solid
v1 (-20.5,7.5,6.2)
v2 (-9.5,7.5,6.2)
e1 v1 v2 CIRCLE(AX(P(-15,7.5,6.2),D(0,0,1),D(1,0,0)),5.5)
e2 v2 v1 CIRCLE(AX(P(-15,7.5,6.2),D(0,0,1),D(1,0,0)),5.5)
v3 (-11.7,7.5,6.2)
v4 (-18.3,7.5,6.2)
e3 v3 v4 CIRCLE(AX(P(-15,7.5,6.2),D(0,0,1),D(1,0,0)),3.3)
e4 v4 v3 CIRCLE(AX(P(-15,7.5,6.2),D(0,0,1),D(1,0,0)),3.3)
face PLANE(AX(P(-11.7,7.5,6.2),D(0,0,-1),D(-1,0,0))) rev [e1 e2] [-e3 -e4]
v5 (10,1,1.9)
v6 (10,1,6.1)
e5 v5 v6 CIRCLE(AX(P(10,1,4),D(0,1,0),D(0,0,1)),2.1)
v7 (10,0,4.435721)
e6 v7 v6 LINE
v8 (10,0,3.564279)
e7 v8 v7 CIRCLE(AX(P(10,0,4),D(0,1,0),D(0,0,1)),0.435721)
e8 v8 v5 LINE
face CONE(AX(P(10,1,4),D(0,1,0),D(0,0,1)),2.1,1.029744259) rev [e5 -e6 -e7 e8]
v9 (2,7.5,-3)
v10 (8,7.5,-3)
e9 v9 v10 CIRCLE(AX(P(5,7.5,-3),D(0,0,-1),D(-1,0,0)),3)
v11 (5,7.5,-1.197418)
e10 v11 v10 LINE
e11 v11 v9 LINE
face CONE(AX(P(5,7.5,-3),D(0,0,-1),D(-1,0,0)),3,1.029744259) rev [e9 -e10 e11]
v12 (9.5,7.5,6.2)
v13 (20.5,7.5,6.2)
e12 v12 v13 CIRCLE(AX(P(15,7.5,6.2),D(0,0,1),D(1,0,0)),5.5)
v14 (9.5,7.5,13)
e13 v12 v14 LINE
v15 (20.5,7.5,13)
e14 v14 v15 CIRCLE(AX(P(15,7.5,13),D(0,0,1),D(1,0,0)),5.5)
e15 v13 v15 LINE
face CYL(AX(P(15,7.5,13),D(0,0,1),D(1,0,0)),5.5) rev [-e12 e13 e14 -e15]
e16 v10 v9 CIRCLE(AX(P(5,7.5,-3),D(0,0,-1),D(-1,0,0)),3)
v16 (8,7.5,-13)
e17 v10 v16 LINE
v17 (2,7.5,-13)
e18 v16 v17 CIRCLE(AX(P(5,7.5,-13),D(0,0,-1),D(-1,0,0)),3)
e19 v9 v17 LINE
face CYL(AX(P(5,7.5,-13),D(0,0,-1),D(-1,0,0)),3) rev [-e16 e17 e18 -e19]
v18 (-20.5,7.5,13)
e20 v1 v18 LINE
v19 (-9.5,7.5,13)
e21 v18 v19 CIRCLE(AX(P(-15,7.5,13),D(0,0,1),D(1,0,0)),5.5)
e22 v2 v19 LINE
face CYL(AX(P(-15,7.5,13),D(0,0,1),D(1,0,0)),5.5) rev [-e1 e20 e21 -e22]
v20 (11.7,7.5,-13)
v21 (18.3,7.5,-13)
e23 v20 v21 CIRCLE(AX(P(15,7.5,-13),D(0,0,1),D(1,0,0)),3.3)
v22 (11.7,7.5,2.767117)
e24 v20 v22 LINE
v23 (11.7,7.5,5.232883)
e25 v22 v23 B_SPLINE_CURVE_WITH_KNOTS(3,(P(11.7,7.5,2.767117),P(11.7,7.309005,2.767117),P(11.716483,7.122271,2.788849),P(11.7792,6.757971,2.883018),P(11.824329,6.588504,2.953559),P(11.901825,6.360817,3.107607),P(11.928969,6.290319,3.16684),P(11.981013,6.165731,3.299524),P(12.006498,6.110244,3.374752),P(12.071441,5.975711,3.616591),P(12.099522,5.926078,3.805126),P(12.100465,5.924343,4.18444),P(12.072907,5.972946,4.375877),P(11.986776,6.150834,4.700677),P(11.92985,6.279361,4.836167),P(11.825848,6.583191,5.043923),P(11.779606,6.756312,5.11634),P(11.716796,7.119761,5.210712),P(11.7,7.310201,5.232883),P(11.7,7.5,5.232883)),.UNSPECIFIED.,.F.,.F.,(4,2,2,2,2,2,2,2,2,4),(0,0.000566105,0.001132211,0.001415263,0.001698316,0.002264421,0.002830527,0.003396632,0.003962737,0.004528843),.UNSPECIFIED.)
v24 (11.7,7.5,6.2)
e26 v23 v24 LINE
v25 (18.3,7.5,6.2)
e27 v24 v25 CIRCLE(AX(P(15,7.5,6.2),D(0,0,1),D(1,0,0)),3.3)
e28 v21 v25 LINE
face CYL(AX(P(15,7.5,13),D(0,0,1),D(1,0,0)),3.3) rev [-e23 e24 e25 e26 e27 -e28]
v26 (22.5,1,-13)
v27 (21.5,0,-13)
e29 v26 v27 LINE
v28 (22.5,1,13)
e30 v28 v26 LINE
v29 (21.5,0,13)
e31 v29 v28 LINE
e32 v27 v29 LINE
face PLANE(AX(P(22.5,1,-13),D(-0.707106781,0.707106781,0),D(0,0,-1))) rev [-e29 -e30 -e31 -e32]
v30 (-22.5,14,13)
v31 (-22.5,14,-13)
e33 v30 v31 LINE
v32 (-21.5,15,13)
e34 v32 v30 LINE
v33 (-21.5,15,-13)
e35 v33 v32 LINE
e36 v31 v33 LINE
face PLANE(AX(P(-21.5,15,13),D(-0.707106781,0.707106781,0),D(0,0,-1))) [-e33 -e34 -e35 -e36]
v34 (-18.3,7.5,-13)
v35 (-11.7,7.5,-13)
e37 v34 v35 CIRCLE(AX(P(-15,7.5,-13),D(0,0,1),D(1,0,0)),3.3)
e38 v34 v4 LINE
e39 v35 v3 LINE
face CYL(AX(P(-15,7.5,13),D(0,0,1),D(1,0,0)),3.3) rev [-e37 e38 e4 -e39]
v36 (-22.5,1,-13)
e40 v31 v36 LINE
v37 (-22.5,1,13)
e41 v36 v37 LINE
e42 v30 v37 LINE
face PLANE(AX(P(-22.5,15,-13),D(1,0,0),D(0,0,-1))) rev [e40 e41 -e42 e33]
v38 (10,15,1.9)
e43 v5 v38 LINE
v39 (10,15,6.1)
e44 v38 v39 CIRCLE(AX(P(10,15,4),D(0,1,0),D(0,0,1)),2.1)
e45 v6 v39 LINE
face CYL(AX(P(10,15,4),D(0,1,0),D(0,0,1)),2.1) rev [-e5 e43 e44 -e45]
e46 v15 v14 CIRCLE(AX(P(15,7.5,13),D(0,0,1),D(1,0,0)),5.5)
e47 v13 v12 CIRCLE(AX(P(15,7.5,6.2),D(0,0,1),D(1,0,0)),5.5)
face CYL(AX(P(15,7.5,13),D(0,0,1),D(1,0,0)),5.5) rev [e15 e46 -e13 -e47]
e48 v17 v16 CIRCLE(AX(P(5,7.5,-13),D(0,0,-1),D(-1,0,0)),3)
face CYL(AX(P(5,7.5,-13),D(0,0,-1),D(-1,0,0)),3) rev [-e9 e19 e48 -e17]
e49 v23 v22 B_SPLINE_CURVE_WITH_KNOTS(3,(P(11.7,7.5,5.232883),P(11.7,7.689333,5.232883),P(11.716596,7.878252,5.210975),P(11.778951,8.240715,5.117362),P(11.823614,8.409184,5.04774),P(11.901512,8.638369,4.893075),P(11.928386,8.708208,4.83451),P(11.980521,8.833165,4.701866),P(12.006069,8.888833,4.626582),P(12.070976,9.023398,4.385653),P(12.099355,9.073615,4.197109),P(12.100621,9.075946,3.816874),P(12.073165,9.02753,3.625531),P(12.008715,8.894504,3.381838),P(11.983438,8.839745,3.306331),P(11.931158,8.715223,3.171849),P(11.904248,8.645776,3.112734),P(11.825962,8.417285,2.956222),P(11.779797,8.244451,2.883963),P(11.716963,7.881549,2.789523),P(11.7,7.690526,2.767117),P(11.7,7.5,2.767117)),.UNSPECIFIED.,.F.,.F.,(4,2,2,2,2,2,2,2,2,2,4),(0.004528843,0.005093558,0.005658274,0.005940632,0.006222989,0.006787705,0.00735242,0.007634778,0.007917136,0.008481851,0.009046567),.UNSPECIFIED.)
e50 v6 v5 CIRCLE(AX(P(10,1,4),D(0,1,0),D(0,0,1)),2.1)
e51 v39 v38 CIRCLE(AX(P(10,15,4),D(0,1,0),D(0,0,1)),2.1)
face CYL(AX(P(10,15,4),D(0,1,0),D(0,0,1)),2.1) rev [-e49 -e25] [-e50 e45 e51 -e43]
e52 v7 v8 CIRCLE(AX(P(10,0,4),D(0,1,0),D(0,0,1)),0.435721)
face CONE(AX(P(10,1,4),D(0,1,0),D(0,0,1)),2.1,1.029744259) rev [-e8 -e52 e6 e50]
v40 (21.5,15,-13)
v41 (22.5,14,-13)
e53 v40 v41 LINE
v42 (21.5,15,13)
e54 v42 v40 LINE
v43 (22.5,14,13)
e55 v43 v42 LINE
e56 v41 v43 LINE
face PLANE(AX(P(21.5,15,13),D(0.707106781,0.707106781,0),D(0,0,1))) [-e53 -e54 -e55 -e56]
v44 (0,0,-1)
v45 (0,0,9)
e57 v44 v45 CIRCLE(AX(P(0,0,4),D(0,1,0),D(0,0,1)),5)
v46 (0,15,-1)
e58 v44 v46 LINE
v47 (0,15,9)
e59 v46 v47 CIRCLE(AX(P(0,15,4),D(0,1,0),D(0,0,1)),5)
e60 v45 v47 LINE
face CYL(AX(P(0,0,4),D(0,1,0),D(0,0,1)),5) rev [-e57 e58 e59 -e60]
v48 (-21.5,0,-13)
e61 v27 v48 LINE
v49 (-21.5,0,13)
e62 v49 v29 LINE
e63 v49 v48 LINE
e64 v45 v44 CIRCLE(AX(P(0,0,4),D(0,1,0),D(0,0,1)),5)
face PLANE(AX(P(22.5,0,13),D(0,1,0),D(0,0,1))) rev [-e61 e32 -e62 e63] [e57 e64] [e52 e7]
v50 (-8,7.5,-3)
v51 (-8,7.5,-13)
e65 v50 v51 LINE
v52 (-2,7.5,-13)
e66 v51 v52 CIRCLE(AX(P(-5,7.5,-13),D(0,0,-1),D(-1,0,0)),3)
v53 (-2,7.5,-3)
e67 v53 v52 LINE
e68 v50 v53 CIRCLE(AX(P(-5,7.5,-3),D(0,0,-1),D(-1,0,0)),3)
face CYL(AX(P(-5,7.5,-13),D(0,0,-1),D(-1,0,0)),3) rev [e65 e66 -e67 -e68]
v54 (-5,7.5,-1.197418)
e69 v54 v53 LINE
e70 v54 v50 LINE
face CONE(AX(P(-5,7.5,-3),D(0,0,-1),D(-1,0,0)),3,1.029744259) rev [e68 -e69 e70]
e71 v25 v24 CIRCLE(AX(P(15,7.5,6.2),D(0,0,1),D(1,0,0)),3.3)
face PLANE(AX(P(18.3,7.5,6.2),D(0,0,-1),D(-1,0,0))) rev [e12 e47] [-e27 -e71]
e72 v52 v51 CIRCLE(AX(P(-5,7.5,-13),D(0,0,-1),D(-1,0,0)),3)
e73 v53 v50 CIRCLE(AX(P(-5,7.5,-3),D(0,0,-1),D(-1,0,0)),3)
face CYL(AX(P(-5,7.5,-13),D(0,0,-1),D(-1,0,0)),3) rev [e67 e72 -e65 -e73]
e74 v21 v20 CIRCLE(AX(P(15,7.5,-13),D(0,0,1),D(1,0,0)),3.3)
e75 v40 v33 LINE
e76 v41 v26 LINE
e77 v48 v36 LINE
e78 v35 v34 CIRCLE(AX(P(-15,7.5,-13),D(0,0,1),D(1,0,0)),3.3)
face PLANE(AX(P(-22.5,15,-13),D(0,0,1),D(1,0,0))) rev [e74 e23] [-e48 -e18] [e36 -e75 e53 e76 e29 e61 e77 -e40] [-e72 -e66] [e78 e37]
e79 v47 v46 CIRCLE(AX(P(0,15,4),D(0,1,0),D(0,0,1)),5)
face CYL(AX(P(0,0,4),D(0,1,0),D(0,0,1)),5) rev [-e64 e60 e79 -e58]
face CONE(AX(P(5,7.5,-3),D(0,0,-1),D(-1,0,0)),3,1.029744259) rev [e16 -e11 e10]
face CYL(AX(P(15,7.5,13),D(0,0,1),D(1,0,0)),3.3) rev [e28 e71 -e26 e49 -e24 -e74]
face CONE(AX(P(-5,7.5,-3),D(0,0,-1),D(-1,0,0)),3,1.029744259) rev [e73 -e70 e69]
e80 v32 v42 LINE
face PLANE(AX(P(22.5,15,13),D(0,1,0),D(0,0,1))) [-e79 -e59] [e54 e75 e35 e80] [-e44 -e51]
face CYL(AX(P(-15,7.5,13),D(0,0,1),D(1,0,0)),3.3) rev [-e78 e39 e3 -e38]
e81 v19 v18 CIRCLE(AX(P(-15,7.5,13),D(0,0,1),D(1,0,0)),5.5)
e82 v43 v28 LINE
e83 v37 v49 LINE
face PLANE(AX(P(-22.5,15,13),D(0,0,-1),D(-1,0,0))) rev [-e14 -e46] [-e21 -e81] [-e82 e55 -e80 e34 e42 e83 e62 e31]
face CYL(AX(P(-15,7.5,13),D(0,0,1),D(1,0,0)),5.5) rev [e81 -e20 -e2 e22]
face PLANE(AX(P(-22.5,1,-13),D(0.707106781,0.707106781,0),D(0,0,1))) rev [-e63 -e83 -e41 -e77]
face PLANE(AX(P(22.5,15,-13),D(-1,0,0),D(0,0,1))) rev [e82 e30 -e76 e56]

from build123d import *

# Parameters (mm, degrees)
SKETCH1_W                                            = 45
SKETCH1_H                                            = 26
BOSS_EXTRUDE1_DEPTH                                  = 15
SKETCH2_R                                            = 5
CUT_EXTRUDE1_DEPTH                                   = 31.004166377
F_6_0MM_DOWEL_HOLE_1_D                               = 6
F_6_0MM_DOWEL_HOLE_1_DEPTH                           = 10
F_6_0MM_DOWEL_HOLE_1_TIP                             = 1.802581857
CHAMFER1_SIZE                                        = 1
CBORE_FOR_M6_HEXAGON_SOCKET_HEAD_CAP_SCR_D           = 6.6
CBORE_FOR_M6_HEXAGON_SOCKET_HEAD_CAP_SCR_CBORE_D     = 11
CBORE_FOR_M6_HEXAGON_SOCKET_HEAD_CAP_SCR_CBORE_DEPTH = 6.8
M5_TAPPED_HOLE1_D                                    = 4.2
M5_TAPPED_HOLE1_DEPTH                                = 14
M5_TAPPED_HOLE1_TIP                                  = 1.2618073


with BuildPart() as part:
    # Sketch1 → Boss-Extrude1 (new body)
    with BuildSketch(Plane(origin=(0, 0, 0), x_dir=(1, 0, 0), z_dir=(0, 1, 0))):
        Rectangle(SKETCH1_W, SKETCH1_H)
    extrude(amount=BOSS_EXTRUDE1_DEPTH)

    # Sketch2 → Cut-Extrude1 (cut, through all)
    with BuildSketch(Plane(origin=(0, 15, 0), x_dir=(1, 0, 0), z_dir=(0, 1, 0))):
        with Locations(Location((0, -4, 0), (0, 0, 270))):
            Circle(SKETCH2_R)
    extrude(amount=-CUT_EXTRUDE1_DEPTH, mode=Mode.SUBTRACT)

    # Ø6.0mm Dowel Hole 1
    with Locations(Plane(origin=(0, 0, -13), x_dir=(-1, 0, 0), z_dir=(0, 0, -1))):
        with Locations((-5, 7.5), (5, 7.5)):
            Hole(F_6_0MM_DOWEL_HOLE_1_D / 2, depth=F_6_0MM_DOWEL_HOLE_1_DEPTH)
            with Locations((0, 0, -(F_6_0MM_DOWEL_HOLE_1_DEPTH + F_6_0MM_DOWEL_HOLE_1_TIP / 2))):  # 118° drill point
                Cone(0, F_6_0MM_DOWEL_HOLE_1_D / 2, F_6_0MM_DOWEL_HOLE_1_TIP, mode=Mode.SUBTRACT)

    # Chamfer1
    chamfer1_edges = [part.edges().sort_by_distance(p)[0] for p in [
        (-22.5, 15, 0),
        (22.5, 15, 0),
        (-22.5, 0, 0),
        (22.5, 0, 0),
    ]]
    chamfer(chamfer1_edges, length=CHAMFER1_SIZE)

    # CBORE for M6 Hexagon socket head cap screws1 (through all)
    with Locations(Plane.XY.offset(13)):
        with Locations((-15, 7.5), (15, 7.5)):
            CounterBoreHole(CBORE_FOR_M6_HEXAGON_SOCKET_HEAD_CAP_SCR_D / 2, CBORE_FOR_M6_HEXAGON_SOCKET_HEAD_CAP_SCR_CBORE_D / 2, CBORE_FOR_M6_HEXAGON_SOCKET_HEAD_CAP_SCR_CBORE_DEPTH)

    # M5 Tapped Hole1
    with Locations(Plane(origin=(0, 15, 0), x_dir=(1, 0, 0), z_dir=(0, 1, 0))):
        with Locations((10, -4)):
            Hole(M5_TAPPED_HOLE1_D / 2, depth=M5_TAPPED_HOLE1_DEPTH)
            with Locations((0, 0, -(M5_TAPPED_HOLE1_DEPTH + M5_TAPPED_HOLE1_TIP / 2))):  # 118° drill point
                Cone(0, M5_TAPPED_HOLE1_D / 2, M5_TAPPED_HOLE1_TIP, mode=Mode.SUBTRACT)


solid = part.part
